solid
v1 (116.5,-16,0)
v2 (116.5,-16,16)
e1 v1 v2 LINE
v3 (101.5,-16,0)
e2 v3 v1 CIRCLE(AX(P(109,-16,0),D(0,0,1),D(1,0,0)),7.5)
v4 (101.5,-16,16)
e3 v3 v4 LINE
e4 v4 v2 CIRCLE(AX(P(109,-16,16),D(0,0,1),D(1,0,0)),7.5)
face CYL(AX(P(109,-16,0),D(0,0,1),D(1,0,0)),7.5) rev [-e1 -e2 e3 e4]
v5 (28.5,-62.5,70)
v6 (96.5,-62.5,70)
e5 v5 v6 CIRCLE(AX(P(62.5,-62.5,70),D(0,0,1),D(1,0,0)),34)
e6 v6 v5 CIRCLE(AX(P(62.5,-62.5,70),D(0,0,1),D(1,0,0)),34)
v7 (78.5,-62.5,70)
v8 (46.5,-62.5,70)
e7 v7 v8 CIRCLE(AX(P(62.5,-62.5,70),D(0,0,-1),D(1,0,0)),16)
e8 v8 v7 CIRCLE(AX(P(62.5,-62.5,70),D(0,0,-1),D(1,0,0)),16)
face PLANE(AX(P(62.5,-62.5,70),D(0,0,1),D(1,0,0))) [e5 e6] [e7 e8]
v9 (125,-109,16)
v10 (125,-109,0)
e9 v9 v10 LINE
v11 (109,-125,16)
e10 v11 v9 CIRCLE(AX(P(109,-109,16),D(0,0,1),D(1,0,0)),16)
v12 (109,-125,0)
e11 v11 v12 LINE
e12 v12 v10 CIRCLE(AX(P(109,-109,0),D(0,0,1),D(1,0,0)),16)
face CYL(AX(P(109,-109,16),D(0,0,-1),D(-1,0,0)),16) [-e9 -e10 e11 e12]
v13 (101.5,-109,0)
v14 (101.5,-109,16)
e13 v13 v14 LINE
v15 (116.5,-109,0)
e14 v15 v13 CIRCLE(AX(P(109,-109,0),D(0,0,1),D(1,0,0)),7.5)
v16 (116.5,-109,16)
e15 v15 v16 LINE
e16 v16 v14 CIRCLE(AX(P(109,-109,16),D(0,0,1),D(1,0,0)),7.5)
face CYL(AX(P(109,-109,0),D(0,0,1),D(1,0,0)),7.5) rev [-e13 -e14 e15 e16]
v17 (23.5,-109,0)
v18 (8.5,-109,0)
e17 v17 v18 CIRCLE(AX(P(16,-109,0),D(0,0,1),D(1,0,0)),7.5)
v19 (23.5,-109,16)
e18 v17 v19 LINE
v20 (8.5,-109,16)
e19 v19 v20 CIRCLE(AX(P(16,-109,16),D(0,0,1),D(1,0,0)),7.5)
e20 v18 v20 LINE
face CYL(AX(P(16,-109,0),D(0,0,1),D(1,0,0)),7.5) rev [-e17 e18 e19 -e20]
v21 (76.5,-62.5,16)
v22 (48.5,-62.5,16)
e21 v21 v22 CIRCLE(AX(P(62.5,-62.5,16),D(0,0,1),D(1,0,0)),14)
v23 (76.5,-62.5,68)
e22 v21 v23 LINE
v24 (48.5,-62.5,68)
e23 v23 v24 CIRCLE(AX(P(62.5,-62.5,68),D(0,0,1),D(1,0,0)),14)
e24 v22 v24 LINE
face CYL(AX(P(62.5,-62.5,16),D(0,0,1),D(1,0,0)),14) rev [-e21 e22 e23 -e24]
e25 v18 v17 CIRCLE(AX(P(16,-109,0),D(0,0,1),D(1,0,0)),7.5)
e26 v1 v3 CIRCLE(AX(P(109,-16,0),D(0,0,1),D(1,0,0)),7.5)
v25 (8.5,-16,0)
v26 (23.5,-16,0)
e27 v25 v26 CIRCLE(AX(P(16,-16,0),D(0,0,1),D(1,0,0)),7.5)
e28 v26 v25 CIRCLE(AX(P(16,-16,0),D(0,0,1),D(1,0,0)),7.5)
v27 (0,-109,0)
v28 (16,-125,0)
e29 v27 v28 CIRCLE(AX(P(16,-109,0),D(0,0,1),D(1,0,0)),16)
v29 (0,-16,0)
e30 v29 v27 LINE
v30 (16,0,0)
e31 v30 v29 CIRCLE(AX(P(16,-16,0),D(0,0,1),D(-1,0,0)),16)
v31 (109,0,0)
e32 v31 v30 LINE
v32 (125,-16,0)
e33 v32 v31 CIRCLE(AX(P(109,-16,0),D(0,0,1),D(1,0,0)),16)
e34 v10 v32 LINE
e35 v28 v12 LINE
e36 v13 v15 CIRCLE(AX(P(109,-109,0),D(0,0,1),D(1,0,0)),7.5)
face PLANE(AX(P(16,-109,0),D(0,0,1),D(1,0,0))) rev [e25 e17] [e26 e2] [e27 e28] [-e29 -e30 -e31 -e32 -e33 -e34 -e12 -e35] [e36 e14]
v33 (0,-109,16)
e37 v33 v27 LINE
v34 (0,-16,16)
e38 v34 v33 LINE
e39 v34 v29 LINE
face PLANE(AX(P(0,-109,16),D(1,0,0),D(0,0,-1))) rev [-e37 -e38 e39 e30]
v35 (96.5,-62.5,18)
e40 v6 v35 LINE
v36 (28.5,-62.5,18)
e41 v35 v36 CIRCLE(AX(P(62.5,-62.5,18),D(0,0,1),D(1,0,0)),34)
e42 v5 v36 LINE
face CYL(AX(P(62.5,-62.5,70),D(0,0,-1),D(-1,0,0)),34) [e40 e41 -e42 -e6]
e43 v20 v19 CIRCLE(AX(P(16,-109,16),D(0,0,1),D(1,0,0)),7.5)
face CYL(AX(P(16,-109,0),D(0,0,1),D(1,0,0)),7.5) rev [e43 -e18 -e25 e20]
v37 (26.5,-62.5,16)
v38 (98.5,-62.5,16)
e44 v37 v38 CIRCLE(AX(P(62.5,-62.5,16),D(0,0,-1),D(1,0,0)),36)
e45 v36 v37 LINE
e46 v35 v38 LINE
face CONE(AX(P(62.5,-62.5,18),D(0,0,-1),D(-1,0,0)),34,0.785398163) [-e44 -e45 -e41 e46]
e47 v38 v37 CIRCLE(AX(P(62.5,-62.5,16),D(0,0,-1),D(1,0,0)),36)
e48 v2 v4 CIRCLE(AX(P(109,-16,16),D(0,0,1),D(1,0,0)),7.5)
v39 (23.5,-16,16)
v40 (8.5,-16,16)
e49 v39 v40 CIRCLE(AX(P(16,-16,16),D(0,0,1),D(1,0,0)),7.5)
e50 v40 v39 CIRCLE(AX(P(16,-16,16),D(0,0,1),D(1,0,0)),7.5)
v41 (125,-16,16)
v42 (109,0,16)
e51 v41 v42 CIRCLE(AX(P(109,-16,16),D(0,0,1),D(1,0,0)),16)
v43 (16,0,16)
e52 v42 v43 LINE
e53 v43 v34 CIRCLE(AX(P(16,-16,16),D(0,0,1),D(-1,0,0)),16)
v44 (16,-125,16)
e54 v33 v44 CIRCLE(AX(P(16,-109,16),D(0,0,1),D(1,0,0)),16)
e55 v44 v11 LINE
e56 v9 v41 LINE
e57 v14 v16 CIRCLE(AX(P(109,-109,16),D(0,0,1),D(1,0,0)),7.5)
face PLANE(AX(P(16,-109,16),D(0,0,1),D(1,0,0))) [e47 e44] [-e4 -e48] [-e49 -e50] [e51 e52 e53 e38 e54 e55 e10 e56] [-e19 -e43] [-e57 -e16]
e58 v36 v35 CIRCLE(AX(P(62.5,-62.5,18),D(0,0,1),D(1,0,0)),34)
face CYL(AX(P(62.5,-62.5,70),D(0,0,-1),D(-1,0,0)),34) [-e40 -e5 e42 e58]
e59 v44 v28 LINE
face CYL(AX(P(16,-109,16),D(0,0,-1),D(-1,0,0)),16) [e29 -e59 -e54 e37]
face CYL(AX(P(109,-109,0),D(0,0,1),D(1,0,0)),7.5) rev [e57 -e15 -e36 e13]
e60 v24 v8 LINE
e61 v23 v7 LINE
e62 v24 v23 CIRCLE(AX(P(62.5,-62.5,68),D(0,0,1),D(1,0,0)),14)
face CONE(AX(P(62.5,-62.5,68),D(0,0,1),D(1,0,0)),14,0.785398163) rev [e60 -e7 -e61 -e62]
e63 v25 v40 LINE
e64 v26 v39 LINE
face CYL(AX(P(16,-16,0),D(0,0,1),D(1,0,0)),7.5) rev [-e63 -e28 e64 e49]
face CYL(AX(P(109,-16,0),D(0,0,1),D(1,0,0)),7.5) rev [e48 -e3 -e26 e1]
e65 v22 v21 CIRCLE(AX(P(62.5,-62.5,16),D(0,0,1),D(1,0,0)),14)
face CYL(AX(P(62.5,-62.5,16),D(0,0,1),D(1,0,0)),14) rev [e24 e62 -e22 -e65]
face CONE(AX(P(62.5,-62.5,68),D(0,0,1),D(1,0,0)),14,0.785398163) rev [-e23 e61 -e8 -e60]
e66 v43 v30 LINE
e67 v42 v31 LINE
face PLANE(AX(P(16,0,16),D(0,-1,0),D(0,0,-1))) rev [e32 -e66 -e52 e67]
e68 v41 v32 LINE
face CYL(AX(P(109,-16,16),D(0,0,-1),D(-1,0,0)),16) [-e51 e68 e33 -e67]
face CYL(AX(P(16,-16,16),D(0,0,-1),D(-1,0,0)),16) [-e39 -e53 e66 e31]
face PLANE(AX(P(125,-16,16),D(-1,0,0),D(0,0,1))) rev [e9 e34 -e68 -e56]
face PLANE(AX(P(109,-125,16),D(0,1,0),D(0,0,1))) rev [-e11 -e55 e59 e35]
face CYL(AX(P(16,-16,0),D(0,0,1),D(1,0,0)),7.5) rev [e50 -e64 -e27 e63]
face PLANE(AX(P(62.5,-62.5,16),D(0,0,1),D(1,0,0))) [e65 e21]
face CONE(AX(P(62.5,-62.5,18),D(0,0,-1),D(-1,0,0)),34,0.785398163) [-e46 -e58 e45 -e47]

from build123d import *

# Parameters (mm, degrees)
FLANGE_PLATE_125X125X16_DEPTH = 16
BOLT_HOLES_SKETCH_R           = 7.5
BOLT_HOLES_4X_15_DEPTH        = 16
HUB_SKETCH_R                  = 34
HUB_68X54_DEPTH               = 54
HUB_CHAMFER_2X45_SIZE         = 2
BORE_SKETCH_R                 = 14
BORE_28_DEPTH                 = 54
BORE_CHAMFER_2X45_SIZE        = 2


with BuildPart() as part:
    # Flange Plate Sketch → Flange Plate 125x125x16 (new body)
    with BuildSketch(Plane.XY):
        with BuildLine():
            Line((16, 0), (109, 0))
            ThreePointArc((109, 0), (120.313708499, -4.686291501), (125, -16))
            Line((125, -16), (125, -109))
            ThreePointArc((125, -109), (120.313708499, -120.313708499), (109, -125))
            Line((109, -125), (16, -125))
            ThreePointArc((16, -125), (4.686291501, -120.313708499), (0, -109))
            Line((0, -109), (0, -16))
            ThreePointArc((0, -16), (4.686291501, -4.686291501), (16, 0))
        make_face()
    extrude(amount=FLANGE_PLATE_125X125X16_DEPTH)

    # Bolt Holes Sketch → Bolt Holes 4xØ15 (cut)
    with BuildSketch(Plane.XY.offset(16)):
        with Locations((16, -16)):
            Circle(BOLT_HOLES_SKETCH_R)
        with Locations((109, -16)):
            Circle(BOLT_HOLES_SKETCH_R)
        with Locations((109, -109)):
            Circle(BOLT_HOLES_SKETCH_R)
        with Locations((16, -109)):
            Circle(BOLT_HOLES_SKETCH_R)
    extrude(amount=-BOLT_HOLES_4X_15_DEPTH, mode=Mode.SUBTRACT)

    # Hub Sketch → Hub Ø68x54 (add)
    with BuildSketch(Plane.XY.offset(16)):
        with Locations((62.5, -62.5)):
            Circle(HUB_SKETCH_R)
    extrude(amount=HUB_68X54_DEPTH)

    # Hub Chamfer 2x45
    hub_chamfer_2x45_edges = [part.edges().sort_by_distance(p)[0] for p in [
        (28.5, -62.5, 16),
    ]]
    chamfer(hub_chamfer_2x45_edges, length=HUB_CHAMFER_2X45_SIZE)

    # Bore Sketch → Bore Ø28 (cut)
    with BuildSketch(Plane.XY.offset(70)):
        with Locations((62.5, -62.5)):
            Circle(BORE_SKETCH_R)
    extrude(amount=-BORE_28_DEPTH, mode=Mode.SUBTRACT)

    # Bore Chamfer 2x45
    bore_chamfer_2x45_edges = [part.edges().sort_by_distance(p)[0] for p in [
        (48.5, -62.5, 70),
    ]]
    chamfer(bore_chamfer_2x45_edges, length=BORE_CHAMFER_2X45_SIZE)


solid = part.part
